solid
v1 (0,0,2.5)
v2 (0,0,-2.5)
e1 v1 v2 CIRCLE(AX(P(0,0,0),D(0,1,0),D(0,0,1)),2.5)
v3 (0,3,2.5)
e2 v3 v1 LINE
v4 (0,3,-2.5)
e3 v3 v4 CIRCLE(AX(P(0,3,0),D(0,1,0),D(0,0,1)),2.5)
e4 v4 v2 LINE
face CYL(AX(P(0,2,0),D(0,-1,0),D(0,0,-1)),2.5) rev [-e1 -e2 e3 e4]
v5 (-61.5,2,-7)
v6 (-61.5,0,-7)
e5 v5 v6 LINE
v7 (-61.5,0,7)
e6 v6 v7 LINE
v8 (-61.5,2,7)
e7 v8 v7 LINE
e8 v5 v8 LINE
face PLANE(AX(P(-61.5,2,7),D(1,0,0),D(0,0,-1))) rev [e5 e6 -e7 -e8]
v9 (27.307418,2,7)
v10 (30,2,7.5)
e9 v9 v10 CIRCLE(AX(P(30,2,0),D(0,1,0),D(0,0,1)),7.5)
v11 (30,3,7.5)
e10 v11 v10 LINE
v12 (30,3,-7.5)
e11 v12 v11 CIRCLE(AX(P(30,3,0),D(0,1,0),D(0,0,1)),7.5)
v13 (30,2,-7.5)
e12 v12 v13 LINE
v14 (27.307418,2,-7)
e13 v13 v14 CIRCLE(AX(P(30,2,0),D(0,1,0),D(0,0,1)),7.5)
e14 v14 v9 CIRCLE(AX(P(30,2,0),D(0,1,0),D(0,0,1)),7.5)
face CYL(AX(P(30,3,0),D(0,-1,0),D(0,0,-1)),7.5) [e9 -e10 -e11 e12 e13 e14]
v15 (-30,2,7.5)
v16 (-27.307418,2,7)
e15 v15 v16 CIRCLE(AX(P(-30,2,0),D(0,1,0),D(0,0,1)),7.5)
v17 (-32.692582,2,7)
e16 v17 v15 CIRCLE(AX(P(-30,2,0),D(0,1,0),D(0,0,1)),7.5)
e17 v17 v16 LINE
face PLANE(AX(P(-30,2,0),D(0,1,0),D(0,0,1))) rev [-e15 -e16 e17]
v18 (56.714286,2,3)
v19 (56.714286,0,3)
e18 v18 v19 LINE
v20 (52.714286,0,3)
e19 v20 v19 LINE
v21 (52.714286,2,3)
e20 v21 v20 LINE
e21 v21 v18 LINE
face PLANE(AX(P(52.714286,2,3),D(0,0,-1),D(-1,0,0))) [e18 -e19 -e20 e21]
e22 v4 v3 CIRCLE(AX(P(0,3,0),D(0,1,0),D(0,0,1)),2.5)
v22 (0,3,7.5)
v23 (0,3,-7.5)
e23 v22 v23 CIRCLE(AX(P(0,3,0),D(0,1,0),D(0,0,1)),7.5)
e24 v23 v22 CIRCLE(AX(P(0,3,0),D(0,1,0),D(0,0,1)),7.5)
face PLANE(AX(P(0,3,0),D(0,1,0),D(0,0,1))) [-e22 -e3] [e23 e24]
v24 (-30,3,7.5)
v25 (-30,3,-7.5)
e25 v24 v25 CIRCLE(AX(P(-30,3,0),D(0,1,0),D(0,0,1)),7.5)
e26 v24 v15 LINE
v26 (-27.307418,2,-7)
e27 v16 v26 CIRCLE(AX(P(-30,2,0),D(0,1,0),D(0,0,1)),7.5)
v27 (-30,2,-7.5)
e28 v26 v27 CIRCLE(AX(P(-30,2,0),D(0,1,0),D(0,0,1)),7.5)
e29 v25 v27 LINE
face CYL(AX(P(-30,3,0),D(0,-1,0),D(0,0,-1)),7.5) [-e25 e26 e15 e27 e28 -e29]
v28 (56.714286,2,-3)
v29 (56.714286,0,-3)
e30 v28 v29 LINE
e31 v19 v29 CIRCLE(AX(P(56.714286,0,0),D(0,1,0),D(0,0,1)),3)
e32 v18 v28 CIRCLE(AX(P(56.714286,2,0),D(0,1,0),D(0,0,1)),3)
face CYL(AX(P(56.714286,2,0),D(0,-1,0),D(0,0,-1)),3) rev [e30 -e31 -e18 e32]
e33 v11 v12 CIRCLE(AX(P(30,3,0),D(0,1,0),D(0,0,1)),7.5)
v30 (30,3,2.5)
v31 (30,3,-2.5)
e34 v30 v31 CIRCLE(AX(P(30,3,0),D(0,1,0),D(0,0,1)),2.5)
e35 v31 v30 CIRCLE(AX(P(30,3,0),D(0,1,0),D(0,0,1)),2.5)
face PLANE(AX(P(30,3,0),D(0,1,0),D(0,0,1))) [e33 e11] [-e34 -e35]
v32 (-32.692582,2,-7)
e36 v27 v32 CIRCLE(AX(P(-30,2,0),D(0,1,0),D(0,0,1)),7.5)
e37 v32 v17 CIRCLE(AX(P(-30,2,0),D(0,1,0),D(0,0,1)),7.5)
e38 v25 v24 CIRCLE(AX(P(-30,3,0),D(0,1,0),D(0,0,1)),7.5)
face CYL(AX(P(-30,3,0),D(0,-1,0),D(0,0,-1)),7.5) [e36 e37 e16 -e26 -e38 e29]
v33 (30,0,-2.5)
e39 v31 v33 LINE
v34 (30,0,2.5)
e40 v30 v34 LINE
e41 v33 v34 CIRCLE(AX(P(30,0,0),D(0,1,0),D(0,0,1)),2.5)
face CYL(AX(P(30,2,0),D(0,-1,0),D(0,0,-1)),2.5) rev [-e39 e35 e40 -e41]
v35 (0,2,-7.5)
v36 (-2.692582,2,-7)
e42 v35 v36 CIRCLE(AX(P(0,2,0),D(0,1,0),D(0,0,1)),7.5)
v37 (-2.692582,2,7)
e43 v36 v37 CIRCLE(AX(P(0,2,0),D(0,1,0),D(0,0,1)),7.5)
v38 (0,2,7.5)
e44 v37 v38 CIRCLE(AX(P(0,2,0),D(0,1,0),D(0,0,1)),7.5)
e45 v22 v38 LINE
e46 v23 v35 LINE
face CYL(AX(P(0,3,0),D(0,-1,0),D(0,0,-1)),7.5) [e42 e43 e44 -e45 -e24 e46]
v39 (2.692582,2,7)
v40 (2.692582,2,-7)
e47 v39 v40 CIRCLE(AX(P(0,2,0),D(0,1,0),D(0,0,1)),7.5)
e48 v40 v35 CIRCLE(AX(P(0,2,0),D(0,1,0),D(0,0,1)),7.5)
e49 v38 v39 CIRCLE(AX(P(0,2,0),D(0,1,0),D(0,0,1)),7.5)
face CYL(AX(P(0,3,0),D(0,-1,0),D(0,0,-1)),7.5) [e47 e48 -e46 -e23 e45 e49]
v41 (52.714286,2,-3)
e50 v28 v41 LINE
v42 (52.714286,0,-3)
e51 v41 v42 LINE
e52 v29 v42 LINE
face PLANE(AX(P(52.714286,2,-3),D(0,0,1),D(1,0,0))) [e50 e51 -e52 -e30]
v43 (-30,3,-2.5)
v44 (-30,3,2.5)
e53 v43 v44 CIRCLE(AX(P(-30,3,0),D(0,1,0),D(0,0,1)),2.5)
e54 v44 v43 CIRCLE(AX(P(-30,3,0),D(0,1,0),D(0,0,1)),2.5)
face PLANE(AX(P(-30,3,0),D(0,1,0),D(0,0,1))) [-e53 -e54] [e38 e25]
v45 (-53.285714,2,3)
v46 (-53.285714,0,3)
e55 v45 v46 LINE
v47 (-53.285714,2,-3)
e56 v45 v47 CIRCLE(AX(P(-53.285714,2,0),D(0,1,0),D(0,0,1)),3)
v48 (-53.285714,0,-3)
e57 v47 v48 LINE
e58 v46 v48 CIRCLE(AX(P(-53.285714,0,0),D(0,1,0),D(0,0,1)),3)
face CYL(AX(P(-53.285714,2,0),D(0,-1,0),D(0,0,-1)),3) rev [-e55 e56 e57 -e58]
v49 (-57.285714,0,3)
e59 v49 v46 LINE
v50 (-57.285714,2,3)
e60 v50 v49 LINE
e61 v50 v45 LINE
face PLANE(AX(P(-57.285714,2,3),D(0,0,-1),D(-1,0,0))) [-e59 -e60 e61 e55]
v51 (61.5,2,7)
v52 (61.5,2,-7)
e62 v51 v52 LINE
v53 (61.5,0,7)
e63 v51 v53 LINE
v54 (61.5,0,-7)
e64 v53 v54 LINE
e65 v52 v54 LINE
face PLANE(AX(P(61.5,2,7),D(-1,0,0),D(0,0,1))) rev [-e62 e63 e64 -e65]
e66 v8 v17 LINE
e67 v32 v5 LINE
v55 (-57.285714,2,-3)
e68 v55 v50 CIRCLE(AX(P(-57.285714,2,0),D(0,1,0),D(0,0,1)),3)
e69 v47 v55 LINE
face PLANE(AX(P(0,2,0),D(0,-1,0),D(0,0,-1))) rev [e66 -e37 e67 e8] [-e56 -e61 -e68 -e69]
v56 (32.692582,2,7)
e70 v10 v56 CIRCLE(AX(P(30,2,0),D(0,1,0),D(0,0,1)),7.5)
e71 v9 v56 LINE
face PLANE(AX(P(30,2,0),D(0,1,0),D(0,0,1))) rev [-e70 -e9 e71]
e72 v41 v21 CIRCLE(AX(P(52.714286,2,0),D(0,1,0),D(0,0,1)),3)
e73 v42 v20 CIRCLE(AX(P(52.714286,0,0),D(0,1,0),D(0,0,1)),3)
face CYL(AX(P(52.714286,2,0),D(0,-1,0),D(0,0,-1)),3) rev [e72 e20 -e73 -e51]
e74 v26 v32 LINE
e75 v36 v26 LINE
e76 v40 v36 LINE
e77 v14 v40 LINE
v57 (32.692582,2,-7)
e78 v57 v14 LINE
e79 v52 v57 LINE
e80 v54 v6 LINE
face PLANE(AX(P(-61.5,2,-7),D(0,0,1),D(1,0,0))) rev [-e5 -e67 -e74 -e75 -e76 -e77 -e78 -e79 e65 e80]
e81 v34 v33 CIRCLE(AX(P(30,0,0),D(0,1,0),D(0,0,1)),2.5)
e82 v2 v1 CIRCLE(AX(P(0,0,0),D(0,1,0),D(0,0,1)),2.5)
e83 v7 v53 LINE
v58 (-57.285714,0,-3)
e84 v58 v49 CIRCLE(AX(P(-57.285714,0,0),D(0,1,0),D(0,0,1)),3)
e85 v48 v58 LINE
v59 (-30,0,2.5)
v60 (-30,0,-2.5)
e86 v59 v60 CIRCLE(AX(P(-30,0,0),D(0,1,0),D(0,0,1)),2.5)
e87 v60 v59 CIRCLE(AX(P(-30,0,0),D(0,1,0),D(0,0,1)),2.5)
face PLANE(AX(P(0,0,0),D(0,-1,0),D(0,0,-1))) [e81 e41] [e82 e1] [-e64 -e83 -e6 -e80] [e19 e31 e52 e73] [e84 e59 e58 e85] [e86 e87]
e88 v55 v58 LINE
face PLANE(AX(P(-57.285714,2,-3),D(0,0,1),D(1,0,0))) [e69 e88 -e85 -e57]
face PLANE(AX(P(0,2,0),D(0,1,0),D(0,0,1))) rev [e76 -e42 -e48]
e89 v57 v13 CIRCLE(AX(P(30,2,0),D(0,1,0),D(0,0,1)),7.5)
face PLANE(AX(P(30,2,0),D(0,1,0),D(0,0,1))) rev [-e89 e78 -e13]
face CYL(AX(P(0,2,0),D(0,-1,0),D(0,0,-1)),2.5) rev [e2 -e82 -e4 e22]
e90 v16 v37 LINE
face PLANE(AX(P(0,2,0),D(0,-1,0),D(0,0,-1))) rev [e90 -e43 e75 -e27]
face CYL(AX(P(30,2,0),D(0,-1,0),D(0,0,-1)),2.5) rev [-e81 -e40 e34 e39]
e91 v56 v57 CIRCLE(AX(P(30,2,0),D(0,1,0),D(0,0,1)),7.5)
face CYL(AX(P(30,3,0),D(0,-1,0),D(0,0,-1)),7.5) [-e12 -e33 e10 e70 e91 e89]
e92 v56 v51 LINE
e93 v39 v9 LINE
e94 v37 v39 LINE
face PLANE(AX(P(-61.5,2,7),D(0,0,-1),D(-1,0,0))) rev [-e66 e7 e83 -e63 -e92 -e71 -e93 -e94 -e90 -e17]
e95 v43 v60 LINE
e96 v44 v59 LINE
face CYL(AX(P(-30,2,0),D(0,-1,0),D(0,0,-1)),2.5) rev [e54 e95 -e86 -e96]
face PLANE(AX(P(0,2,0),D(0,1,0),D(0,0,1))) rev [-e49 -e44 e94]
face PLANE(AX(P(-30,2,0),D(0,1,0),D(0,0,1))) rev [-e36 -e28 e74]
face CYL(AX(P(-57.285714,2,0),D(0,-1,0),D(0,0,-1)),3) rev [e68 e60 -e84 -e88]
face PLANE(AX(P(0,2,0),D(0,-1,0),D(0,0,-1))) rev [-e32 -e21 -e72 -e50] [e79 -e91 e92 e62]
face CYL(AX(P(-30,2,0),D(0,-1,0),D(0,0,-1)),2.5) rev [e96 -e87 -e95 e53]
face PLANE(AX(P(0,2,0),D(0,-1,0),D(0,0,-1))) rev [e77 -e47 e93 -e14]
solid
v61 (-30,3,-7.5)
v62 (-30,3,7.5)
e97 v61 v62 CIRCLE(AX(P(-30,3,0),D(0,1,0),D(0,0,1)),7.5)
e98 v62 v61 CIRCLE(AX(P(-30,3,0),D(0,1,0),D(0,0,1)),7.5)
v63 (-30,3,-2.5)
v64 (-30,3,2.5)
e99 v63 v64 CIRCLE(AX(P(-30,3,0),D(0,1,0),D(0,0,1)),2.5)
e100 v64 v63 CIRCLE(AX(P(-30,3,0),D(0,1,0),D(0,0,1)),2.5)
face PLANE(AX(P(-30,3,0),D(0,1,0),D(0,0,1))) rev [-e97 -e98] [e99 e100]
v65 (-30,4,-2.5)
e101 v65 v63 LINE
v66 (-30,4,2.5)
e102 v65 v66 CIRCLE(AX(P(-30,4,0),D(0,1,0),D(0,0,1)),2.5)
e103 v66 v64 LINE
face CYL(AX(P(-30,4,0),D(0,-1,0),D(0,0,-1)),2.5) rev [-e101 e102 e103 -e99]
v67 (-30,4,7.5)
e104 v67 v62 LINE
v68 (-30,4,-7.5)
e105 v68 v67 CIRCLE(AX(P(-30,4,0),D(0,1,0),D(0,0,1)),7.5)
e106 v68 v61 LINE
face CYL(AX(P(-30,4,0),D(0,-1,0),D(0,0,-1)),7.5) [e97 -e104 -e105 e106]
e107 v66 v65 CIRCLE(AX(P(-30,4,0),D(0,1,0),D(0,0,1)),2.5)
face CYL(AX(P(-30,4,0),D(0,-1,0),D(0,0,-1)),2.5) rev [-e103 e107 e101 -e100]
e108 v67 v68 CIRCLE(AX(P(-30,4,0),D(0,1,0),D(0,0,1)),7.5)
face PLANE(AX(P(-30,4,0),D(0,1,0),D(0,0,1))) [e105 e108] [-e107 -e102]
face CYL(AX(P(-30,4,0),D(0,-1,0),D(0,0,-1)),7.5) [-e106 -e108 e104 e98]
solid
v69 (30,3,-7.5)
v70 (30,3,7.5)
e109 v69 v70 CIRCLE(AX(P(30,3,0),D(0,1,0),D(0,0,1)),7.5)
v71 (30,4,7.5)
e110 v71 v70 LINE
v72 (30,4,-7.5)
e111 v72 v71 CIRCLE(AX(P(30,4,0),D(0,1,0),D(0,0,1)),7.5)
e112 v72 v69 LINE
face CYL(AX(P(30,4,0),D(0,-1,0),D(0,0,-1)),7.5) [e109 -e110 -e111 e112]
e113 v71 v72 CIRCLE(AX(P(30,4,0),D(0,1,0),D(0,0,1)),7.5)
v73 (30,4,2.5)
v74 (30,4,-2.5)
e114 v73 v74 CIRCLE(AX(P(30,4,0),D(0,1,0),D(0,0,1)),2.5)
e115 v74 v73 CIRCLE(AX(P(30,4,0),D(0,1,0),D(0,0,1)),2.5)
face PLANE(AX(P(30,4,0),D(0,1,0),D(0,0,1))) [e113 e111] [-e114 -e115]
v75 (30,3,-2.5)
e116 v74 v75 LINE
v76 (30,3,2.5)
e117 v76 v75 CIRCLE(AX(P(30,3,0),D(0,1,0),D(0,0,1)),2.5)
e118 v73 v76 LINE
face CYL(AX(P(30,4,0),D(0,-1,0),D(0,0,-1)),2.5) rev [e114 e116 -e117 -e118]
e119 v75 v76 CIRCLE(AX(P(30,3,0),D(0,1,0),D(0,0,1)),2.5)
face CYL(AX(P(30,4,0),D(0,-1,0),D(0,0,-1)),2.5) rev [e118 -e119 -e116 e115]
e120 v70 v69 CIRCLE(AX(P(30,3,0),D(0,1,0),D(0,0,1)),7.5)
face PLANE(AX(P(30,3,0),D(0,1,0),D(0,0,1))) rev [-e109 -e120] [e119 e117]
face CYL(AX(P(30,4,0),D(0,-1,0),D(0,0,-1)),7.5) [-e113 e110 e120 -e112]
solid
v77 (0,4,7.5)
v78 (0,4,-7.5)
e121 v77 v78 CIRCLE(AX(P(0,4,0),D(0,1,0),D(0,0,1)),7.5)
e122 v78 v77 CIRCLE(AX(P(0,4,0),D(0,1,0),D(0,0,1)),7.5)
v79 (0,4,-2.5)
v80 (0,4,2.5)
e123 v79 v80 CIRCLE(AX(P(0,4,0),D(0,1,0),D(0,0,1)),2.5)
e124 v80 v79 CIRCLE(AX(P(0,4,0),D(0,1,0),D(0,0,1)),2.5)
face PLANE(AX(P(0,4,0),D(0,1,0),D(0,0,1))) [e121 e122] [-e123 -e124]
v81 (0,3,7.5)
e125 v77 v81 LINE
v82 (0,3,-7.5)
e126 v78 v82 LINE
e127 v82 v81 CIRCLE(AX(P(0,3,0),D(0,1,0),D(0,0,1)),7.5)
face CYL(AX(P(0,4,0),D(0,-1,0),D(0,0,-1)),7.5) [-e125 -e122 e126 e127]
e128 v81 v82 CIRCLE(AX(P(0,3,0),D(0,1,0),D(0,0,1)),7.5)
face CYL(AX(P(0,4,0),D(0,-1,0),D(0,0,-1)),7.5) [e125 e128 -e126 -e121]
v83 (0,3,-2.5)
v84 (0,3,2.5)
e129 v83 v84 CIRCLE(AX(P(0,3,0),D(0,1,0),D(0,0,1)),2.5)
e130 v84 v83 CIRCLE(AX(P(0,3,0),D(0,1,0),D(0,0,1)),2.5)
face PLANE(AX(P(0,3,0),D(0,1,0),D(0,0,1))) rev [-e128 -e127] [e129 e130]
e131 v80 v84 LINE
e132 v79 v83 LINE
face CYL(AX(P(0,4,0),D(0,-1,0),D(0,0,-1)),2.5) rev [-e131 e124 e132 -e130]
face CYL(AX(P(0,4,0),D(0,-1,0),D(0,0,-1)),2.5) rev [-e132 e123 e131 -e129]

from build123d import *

# Parameters (mm, degrees)
SKETCH_1_W        = 123
SKETCH_1_H        = 14
SKETCH_1_R        = 2.5
EXTRUDE_1_DEPTH   = 2
SKETCH_2_R        = 7.5
SKETCH_2_R_2      = 2.5
EXTRUDE_2_DEPTH   = 1
SKETCH_3_R        = 7.5
SKETCH_3_R_2      = 2.5
EXTRUDE_3_DEPTH   = 1
EXTRUDE_3_2_DEPTH = 1
EXTRUDE_3_3_DEPTH = 1


with BuildPart() as part:
    # 草图1 → 凸台-拉伸1 (new body)
    with BuildSketch(Plane(origin=(0, 0, 0), x_dir=(1, 0, 0), z_dir=(0, 1, 0))):
        Rectangle(SKETCH_1_W, SKETCH_1_H)
        with Locations(Location((-30, 0, 0), (0, 0, 270))):
            Circle(SKETCH_1_R, mode=Mode.SUBTRACT)
        with Locations(Location((0, 0, 0), (0, 0, 270))):
            Circle(SKETCH_1_R, mode=Mode.SUBTRACT)
        with Locations(Location((30, 0, 0), (0, 0, 270))):
            Circle(SKETCH_1_R, mode=Mode.SUBTRACT)
        with BuildLine():
            Line((-57.285714286, 3), (-53.285714286, 3))
            ThreePointArc((-53.285714286, 3), (-50.285714286, 0), (-53.285714286, -3))
            Line((-53.285714286, -3), (-57.285714286, -3))
            ThreePointArc((-57.285714286, -3), (-60.285714286, 0), (-57.285714286, 3))
        make_face(mode=Mode.SUBTRACT)
        with BuildLine():
            Line((52.714285714, 3), (56.714285714, 3))
            ThreePointArc((56.714285714, 3), (59.714285714, 0), (56.714285714, -3))
            Line((56.714285714, -3), (52.714285714, -3))
            ThreePointArc((52.714285714, -3), (49.714285714, 0), (52.714285714, 3))
        make_face(mode=Mode.SUBTRACT)
    extrude(amount=EXTRUDE_1_DEPTH)

    # 草图2 → 凸台-拉伸2 (add)
    # profile 1 of 3: a face of its own
    with BuildSketch(Plane(origin=(0, 2, 0), x_dir=(1, 0, 0), z_dir=(0, 1, 0))):
        with Locations(Location((-30, 0, 0), (0, 0, 68.960530219))):
            Circle(SKETCH_2_R)
        with Locations(Location((-30, 0, 0), (0, 0, 270))):
            Circle(SKETCH_2_R_2, mode=Mode.SUBTRACT)
    # profile 2 of 3: a face of its own
    with BuildSketch(Plane(origin=(0, 2, 0), x_dir=(1, 0, 0), z_dir=(0, 1, 0))):
        with Locations(Location((0, 0, 0), (0, 0, 111.039469781))):
            Circle(SKETCH_2_R)
        with Locations(Location((0, 0, 0), (0, 0, 270))):
            Circle(SKETCH_2_R_2, mode=Mode.SUBTRACT)
    # profile 3 of 3: a face of its own
    with BuildSketch(Plane(origin=(0, 2, 0), x_dir=(1, 0, 0), z_dir=(0, 1, 0))):
        with Locations(Location((30, 0, 0), (0, 0, 68.960530219))):
            Circle(SKETCH_2_R)
        with Locations(Location((30, 0, 0), (0, 0, 270))):
            Circle(SKETCH_2_R_2, mode=Mode.SUBTRACT)
    extrude(amount=EXTRUDE_2_DEPTH)


with BuildPart() as body_2:
    # 草图3 → 凸台-拉伸3 (new body)
    with BuildSketch(Plane(origin=(0, 3, 0), x_dir=(1, 0, 0), z_dir=(0, 1, 0))):
        with Locations(Location((-30, 0, 0), (0, 0, 270))):
            Circle(SKETCH_3_R)
        with Locations(Location((-30, 0, 0), (0, 0, 270))):
            Circle(SKETCH_3_R_2, mode=Mode.SUBTRACT)
    extrude(amount=EXTRUDE_3_DEPTH)


with BuildPart() as body_3:
    # 草图3 → Extrude 3 2 (new body)
    with BuildSketch(Plane(origin=(0, 3, 0), x_dir=(1, 0, 0), z_dir=(0, 1, 0))):
        with Locations(Location((0, 0, 0), (0, 0, 270))):
            Circle(SKETCH_3_R)
        with Locations(Location((0, 0, 0), (0, 0, 270))):
            Circle(SKETCH_3_R_2, mode=Mode.SUBTRACT)
    extrude(amount=EXTRUDE_3_2_DEPTH)


with BuildPart() as body_4:
    # 草图3 → Extrude 3 3 (new body)
    with BuildSketch(Plane(origin=(0, 3, 0), x_dir=(1, 0, 0), z_dir=(0, 1, 0))):
        with Locations(Location((30, 0, 0), (0, 0, 270))):
            Circle(SKETCH_3_R)
        with Locations(Location((30, 0, 0), (0, 0, 270))):
            Circle(SKETCH_3_R_2, mode=Mode.SUBTRACT)
    extrude(amount=EXTRUDE_3_3_DEPTH)


solid = Compound([part.part, body_2.part, body_3.part, body_4.part])
